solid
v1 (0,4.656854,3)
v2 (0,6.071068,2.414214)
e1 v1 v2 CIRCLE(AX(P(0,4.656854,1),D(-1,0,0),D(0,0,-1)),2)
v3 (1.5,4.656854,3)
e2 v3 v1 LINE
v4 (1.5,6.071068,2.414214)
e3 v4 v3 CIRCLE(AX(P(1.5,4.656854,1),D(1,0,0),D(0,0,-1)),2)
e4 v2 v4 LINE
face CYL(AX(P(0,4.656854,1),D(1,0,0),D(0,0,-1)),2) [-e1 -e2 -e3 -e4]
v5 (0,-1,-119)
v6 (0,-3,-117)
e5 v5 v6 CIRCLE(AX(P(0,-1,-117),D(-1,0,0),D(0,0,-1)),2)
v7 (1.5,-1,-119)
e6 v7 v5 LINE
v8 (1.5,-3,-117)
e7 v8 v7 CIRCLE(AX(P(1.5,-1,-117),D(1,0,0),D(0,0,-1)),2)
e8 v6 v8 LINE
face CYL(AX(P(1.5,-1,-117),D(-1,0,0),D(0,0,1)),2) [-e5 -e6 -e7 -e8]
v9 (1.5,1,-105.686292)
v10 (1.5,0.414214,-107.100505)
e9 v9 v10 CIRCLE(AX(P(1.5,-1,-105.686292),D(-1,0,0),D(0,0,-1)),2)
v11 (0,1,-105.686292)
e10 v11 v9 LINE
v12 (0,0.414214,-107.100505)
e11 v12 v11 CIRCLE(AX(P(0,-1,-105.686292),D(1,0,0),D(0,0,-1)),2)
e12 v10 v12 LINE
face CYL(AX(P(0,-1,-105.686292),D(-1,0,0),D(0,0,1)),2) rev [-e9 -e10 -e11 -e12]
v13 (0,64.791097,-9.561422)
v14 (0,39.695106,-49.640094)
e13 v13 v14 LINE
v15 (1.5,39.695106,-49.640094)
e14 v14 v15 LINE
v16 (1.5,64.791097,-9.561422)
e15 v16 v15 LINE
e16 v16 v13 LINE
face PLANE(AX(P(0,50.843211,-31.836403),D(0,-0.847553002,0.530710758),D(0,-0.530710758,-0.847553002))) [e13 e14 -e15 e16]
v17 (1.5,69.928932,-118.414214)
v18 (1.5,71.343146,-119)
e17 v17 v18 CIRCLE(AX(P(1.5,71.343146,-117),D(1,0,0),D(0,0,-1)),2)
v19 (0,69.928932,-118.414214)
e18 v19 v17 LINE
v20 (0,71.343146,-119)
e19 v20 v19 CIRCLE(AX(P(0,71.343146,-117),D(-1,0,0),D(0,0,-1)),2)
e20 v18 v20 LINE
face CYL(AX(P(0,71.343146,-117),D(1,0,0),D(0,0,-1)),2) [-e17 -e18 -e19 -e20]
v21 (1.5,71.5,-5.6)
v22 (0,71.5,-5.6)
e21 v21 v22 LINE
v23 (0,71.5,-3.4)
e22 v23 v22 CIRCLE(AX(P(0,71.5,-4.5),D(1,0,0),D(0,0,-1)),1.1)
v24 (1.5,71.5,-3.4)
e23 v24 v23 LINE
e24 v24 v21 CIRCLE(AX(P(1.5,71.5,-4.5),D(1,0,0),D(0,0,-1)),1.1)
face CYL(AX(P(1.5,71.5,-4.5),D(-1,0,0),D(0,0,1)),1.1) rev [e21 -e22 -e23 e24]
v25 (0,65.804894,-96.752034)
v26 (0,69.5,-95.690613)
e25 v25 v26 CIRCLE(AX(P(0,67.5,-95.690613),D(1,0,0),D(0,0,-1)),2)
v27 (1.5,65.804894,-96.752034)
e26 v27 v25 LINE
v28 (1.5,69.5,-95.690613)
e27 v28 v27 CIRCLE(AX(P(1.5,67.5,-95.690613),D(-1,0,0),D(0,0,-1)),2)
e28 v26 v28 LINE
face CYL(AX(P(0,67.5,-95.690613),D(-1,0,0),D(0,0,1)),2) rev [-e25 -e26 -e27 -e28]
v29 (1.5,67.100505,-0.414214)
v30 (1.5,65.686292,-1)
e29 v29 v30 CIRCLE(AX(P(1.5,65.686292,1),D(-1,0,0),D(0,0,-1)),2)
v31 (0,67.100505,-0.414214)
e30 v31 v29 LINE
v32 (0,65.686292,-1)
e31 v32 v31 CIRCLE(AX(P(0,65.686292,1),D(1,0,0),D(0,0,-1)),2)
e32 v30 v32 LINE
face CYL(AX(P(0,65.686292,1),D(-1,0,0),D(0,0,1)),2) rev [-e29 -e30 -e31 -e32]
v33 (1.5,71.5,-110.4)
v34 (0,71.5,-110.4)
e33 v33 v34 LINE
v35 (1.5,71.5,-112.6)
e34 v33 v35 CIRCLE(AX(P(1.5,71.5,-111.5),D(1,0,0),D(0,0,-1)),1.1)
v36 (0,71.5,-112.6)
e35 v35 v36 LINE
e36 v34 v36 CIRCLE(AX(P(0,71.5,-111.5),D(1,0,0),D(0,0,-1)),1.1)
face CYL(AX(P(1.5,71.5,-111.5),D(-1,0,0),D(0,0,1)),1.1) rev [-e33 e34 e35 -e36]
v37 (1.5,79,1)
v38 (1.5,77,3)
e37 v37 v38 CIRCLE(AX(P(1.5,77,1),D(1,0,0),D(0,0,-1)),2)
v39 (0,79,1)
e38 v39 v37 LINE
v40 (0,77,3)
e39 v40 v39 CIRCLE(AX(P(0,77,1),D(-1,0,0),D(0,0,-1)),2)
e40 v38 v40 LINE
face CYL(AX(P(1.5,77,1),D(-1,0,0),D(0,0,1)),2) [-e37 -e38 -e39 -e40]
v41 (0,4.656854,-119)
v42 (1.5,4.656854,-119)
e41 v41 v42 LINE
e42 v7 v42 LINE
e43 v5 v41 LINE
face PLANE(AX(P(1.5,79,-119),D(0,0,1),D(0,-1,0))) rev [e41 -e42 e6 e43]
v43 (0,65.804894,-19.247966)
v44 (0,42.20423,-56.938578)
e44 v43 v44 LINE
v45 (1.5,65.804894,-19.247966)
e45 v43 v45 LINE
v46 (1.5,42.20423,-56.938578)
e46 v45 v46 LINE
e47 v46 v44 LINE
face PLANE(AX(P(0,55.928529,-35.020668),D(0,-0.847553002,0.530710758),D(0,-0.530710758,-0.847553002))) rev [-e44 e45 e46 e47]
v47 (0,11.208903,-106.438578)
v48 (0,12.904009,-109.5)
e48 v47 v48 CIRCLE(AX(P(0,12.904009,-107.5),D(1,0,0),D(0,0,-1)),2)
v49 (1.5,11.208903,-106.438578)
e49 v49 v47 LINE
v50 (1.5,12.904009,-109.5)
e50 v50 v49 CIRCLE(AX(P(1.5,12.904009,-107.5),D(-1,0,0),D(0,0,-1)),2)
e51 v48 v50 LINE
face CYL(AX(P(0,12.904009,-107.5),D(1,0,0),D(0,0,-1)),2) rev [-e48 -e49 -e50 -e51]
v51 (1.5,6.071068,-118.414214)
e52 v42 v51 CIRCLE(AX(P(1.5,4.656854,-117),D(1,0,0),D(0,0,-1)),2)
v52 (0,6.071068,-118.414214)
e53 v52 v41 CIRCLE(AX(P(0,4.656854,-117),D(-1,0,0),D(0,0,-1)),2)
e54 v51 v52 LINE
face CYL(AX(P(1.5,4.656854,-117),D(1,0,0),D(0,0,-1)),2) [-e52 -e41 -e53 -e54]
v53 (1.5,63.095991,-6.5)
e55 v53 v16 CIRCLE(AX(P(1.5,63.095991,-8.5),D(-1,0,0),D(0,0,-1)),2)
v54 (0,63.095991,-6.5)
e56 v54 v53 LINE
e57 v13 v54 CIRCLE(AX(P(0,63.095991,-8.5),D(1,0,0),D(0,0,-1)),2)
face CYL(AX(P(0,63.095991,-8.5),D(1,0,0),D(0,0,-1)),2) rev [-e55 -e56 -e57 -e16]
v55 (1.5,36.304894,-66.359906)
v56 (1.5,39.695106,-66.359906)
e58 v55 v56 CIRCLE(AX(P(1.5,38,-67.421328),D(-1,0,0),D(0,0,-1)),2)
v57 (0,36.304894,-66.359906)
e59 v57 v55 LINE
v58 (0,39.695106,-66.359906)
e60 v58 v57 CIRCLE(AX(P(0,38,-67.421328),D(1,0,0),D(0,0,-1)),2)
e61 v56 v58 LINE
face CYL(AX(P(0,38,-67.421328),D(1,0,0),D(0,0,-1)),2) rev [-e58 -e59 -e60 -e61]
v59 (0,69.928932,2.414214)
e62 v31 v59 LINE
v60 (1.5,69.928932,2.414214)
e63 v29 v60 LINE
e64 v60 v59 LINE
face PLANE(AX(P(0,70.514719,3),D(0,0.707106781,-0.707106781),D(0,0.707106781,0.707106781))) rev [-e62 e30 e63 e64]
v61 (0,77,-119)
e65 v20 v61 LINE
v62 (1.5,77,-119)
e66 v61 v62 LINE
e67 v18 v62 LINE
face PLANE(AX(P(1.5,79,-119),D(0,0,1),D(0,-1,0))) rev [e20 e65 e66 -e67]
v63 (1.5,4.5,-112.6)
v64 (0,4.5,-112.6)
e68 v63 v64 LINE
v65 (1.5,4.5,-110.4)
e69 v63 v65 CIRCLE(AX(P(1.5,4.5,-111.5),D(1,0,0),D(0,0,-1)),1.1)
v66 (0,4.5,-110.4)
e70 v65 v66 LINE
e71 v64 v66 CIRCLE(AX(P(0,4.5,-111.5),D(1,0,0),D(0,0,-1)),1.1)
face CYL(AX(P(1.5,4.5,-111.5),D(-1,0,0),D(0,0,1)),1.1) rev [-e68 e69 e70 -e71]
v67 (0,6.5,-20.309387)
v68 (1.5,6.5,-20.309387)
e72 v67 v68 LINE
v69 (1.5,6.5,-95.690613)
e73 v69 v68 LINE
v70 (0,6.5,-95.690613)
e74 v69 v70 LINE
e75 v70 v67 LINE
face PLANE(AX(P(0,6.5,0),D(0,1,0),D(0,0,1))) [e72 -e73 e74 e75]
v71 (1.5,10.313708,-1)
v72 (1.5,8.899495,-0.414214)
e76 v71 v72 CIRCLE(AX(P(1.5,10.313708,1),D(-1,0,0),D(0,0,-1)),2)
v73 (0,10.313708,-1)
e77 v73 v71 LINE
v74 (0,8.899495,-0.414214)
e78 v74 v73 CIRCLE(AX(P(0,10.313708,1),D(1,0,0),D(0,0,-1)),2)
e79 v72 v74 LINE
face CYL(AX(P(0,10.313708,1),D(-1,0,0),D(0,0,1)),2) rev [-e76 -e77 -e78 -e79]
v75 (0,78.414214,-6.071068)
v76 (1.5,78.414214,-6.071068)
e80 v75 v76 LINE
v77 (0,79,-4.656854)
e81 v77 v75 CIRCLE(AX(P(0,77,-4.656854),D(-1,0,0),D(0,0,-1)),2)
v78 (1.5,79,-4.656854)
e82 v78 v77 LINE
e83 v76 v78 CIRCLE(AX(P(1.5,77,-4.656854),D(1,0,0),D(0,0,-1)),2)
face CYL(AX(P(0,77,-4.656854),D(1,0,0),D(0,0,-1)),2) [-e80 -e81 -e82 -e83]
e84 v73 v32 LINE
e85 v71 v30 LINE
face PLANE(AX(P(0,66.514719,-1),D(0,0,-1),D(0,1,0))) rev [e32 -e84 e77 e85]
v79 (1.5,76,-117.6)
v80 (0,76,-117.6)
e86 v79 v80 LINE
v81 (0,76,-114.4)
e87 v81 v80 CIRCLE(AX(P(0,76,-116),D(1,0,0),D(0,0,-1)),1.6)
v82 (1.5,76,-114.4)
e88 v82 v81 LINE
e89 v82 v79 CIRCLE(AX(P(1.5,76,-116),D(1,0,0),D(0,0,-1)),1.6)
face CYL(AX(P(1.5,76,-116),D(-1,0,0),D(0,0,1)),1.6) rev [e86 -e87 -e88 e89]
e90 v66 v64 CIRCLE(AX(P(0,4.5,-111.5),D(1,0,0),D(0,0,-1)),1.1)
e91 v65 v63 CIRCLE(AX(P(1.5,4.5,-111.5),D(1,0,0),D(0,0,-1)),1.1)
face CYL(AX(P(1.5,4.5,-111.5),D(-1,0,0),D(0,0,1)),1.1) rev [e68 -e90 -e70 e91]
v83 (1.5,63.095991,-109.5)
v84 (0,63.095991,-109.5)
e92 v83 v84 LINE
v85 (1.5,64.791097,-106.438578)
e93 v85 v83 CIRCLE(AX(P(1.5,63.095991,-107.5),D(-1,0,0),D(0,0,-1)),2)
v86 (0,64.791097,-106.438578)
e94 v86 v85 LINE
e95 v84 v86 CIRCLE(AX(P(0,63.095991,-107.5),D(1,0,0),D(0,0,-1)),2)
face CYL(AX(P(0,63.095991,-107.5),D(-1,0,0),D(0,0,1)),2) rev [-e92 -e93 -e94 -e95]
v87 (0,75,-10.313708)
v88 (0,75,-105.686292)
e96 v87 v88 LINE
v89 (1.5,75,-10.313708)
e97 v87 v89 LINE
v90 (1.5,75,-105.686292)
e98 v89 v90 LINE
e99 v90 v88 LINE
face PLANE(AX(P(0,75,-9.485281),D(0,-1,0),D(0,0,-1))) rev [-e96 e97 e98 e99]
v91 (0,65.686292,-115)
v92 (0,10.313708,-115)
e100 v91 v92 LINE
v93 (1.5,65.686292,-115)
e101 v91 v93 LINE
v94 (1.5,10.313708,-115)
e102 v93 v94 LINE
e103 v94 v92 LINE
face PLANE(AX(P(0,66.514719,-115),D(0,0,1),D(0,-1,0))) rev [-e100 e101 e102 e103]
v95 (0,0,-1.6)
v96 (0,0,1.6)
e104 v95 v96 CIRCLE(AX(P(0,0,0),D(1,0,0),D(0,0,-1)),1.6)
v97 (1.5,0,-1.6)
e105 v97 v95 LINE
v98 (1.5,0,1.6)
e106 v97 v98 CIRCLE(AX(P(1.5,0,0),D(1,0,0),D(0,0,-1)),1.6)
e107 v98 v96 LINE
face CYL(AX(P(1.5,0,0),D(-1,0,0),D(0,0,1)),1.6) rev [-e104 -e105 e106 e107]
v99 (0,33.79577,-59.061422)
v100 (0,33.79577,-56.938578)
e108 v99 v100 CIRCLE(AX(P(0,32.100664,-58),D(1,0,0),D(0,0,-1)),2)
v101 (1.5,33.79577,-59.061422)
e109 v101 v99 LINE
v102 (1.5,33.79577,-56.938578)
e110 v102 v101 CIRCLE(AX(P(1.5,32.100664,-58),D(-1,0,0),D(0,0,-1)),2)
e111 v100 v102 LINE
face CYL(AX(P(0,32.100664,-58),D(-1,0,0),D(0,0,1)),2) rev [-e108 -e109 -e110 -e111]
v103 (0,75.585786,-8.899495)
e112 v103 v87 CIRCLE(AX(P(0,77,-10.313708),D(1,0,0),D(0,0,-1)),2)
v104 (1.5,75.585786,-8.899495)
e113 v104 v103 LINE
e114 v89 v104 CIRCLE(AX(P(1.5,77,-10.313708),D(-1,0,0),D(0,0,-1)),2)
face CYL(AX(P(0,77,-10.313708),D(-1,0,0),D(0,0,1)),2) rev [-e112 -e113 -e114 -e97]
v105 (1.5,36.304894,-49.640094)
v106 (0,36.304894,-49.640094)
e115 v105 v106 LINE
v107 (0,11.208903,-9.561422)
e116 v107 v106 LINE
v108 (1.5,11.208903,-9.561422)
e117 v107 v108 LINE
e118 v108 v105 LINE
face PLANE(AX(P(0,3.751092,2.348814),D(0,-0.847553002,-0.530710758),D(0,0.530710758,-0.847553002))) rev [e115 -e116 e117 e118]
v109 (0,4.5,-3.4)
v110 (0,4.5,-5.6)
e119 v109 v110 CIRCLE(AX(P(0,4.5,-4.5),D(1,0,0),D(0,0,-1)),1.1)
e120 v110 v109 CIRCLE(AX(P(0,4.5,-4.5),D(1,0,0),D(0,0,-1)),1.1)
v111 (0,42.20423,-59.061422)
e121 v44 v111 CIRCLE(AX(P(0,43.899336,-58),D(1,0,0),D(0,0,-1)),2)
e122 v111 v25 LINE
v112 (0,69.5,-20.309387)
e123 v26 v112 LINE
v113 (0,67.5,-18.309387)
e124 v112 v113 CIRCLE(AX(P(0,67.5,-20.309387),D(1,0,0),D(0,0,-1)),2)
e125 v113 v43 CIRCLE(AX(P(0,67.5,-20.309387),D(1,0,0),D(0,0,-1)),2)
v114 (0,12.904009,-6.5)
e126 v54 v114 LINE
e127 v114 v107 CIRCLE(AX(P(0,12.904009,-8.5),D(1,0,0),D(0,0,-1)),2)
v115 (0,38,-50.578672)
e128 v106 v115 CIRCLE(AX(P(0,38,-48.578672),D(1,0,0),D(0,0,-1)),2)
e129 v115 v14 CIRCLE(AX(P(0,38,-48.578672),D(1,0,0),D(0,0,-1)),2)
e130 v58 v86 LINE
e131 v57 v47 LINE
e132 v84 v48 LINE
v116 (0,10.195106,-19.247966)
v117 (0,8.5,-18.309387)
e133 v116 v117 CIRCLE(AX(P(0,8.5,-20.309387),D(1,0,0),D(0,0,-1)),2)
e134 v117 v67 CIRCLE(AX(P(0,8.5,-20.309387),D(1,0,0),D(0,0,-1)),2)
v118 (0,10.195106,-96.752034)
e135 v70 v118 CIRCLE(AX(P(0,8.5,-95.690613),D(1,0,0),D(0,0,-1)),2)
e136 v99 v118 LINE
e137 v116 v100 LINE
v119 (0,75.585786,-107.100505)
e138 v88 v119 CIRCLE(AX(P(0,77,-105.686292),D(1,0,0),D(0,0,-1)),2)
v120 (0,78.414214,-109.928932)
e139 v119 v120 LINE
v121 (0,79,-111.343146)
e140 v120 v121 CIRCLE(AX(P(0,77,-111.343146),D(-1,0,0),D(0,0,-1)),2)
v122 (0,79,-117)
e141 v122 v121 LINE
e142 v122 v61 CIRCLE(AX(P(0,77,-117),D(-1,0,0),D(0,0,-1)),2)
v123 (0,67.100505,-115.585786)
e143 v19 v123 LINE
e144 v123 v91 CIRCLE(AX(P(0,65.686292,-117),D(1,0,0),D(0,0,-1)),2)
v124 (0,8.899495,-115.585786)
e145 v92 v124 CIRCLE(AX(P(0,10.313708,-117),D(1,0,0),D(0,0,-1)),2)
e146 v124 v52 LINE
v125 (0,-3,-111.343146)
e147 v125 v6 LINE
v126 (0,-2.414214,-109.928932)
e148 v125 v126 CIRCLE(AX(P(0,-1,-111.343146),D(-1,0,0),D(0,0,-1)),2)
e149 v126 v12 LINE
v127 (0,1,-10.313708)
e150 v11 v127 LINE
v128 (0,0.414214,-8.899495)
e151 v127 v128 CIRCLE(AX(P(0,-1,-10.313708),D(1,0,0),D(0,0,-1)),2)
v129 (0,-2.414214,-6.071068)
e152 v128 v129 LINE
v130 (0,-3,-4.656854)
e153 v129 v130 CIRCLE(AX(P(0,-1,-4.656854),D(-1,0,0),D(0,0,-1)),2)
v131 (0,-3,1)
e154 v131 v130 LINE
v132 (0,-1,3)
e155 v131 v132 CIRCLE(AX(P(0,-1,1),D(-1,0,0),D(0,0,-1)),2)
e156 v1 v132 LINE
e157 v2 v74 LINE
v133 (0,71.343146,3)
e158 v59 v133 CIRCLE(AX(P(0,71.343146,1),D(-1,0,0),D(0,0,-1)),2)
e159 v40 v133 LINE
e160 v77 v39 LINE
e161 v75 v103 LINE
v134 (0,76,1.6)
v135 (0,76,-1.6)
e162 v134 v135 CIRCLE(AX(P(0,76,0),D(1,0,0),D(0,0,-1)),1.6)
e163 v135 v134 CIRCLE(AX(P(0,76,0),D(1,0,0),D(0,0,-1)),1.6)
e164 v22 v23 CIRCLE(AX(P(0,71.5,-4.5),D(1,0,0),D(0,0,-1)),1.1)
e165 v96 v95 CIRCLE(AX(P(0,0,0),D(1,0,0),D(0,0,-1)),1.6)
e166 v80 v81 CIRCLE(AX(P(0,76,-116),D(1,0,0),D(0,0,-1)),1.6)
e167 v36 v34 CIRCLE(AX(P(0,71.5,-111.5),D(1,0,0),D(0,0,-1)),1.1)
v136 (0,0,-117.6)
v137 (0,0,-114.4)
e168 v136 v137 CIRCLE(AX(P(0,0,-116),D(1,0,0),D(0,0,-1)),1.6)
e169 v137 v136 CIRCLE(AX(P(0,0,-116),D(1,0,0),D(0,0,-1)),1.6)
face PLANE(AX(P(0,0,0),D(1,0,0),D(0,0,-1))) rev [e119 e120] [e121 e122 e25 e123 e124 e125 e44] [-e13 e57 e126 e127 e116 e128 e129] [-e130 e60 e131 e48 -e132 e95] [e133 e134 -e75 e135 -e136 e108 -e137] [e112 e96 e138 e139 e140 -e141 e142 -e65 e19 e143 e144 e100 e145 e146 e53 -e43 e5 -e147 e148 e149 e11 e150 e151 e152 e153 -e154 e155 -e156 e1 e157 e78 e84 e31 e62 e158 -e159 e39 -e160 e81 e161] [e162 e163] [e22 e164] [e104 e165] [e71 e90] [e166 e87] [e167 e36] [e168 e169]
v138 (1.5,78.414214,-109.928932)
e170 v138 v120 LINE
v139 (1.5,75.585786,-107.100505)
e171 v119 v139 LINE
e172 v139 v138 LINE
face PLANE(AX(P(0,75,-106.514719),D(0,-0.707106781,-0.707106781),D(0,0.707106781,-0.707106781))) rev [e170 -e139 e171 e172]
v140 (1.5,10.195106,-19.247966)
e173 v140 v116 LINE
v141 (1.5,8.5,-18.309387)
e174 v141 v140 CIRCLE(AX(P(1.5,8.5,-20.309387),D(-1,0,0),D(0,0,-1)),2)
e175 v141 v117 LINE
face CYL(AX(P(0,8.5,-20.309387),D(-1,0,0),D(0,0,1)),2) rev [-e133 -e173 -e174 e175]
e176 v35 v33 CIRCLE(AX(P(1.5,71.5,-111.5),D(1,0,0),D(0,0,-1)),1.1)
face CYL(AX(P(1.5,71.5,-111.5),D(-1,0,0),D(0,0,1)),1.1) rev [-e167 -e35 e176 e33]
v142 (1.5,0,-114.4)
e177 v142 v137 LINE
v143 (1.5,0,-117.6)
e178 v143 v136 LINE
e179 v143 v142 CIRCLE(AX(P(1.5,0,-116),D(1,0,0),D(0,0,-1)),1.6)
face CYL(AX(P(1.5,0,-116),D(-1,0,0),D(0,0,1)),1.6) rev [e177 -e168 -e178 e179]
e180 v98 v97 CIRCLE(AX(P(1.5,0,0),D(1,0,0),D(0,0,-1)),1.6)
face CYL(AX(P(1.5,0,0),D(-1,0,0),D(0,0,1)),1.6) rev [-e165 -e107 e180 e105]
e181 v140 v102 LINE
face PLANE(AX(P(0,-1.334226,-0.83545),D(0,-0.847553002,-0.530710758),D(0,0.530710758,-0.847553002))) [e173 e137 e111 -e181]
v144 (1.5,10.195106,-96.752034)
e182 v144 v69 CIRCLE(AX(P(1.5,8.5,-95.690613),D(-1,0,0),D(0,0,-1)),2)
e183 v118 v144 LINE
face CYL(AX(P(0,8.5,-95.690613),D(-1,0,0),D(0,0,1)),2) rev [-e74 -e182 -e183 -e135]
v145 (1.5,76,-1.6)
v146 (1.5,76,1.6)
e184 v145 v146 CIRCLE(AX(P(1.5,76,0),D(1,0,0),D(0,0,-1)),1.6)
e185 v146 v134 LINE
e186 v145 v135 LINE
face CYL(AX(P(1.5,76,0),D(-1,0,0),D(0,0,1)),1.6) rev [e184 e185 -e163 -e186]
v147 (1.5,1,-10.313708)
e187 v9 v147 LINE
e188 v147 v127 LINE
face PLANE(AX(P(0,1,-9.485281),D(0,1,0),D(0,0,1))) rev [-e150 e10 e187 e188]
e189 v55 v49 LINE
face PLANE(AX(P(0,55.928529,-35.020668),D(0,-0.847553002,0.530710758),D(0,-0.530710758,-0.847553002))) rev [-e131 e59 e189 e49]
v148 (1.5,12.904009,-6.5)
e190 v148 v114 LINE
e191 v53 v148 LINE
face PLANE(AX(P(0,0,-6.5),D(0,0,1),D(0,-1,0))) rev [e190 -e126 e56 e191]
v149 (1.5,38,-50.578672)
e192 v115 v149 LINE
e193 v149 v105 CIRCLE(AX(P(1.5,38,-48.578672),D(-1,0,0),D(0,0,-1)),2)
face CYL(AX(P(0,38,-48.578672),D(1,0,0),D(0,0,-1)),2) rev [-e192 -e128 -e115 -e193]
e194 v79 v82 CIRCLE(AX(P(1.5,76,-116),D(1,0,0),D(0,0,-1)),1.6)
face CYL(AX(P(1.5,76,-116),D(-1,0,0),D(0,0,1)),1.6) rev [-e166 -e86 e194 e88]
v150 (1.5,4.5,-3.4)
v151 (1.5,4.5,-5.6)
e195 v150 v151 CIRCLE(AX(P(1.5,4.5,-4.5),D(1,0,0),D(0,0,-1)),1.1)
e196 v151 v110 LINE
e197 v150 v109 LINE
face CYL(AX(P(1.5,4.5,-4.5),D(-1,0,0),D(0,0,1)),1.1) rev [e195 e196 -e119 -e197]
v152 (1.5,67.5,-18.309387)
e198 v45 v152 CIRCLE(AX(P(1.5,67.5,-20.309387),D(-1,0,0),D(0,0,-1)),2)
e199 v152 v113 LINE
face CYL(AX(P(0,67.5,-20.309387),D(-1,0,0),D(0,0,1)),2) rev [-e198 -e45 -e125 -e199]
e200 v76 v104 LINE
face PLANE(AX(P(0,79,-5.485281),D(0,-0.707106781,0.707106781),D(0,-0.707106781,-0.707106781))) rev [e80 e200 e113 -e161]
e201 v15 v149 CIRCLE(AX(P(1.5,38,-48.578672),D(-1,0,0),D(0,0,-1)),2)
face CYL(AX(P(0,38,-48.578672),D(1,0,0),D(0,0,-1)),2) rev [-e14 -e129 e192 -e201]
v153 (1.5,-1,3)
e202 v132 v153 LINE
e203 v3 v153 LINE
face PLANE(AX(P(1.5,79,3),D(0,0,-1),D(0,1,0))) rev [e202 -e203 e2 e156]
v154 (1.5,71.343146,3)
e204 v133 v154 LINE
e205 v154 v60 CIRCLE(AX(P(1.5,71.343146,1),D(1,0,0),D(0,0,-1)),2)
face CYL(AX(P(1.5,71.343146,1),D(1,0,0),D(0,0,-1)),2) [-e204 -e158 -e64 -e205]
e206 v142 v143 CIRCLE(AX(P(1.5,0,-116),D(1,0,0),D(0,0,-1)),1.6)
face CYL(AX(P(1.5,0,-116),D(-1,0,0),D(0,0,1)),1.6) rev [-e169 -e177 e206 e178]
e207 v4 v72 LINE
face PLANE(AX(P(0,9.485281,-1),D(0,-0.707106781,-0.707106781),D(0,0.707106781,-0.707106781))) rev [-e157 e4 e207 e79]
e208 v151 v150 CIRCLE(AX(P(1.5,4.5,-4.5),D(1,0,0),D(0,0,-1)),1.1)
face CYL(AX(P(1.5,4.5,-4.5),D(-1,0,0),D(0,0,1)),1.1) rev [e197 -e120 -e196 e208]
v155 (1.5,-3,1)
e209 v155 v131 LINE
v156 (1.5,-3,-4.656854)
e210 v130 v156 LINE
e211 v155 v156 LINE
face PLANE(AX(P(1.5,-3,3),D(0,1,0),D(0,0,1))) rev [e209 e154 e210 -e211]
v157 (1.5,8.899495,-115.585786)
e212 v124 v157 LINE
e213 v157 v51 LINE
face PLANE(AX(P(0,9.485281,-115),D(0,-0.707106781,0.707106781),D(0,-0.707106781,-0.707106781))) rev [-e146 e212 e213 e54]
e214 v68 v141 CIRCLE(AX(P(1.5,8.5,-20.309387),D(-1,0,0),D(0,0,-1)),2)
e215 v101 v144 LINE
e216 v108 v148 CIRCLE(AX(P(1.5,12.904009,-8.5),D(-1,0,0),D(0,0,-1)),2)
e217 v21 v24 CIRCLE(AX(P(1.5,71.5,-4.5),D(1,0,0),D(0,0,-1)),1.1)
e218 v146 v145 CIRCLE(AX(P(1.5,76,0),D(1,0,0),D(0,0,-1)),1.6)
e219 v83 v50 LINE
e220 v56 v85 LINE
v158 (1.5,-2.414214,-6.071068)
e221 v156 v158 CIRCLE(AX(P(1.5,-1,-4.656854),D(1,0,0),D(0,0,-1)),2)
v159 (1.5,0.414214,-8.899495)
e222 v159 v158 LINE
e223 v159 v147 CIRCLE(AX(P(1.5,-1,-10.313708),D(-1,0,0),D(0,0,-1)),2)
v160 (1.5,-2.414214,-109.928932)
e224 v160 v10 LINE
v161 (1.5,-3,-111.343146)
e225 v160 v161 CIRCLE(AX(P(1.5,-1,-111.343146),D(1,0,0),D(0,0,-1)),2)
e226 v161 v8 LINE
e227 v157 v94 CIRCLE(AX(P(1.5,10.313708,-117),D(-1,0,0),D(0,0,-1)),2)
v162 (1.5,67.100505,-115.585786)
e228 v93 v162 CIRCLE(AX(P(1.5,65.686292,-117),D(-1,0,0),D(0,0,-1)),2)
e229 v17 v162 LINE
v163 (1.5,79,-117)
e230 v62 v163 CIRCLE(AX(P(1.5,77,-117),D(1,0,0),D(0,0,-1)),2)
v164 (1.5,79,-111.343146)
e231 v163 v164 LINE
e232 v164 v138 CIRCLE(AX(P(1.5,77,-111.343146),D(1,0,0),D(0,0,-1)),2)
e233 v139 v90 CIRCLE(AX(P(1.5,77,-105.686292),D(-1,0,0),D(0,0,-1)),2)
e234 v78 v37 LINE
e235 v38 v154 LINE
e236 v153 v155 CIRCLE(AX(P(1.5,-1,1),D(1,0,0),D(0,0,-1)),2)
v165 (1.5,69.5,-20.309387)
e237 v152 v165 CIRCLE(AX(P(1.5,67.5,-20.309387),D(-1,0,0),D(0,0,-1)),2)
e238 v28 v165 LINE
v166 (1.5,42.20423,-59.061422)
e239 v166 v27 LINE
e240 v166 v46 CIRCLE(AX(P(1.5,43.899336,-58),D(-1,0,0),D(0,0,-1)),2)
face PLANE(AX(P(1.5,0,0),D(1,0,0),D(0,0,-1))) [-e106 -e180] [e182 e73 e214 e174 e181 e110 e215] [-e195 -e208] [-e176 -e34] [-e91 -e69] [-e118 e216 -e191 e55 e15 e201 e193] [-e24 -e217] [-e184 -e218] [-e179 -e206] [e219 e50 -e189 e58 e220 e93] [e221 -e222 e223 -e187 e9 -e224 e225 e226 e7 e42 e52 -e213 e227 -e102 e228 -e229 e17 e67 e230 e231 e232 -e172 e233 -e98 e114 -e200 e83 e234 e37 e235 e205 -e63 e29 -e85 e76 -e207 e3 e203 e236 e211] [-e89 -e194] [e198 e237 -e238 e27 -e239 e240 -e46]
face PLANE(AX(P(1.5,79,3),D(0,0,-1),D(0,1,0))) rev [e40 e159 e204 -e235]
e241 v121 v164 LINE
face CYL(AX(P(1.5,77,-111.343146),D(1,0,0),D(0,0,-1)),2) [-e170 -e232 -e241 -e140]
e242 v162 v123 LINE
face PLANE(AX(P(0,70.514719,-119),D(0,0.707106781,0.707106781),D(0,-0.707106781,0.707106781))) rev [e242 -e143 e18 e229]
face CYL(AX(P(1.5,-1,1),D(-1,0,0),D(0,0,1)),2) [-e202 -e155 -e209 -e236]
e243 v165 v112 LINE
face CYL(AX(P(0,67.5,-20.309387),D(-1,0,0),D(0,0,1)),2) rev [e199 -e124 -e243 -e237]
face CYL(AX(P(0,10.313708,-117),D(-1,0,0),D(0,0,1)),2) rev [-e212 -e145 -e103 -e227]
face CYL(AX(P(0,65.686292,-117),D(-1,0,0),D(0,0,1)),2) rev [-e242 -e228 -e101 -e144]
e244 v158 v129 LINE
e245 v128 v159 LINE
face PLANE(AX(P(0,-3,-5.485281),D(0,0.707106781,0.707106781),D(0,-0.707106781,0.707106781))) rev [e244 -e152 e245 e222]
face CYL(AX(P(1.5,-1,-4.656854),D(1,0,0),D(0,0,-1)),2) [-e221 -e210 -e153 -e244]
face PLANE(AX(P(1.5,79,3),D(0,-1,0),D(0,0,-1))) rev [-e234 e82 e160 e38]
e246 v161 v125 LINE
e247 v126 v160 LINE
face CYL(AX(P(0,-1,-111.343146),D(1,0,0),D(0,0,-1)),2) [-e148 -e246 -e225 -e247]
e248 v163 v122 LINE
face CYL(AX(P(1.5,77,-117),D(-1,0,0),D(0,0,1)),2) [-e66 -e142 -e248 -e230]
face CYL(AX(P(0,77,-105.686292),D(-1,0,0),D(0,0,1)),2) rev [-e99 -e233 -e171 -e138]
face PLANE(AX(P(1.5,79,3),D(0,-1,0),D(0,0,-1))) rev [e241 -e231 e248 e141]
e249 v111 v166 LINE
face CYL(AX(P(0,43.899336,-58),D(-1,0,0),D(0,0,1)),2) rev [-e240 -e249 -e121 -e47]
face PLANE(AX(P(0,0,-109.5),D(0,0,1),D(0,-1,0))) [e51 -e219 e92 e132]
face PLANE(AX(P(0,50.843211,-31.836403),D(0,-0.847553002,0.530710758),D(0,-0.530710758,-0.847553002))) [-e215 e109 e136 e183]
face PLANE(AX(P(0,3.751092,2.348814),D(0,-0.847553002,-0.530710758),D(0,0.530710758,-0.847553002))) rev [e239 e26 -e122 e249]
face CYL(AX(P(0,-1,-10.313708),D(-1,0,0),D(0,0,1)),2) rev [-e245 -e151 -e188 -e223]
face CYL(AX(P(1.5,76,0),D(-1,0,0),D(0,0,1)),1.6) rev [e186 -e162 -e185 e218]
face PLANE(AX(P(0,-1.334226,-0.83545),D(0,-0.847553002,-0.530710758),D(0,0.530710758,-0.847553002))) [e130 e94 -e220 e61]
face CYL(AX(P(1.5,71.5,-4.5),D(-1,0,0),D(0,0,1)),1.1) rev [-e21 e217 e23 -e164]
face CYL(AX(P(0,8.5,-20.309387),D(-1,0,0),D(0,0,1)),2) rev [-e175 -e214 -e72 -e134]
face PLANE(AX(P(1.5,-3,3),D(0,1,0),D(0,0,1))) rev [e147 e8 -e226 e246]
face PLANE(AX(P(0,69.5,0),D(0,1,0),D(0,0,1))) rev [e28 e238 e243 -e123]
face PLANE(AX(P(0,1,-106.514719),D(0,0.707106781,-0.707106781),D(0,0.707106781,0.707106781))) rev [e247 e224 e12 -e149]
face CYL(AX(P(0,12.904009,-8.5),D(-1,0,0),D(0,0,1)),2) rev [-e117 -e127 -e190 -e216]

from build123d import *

# Parameters (mm, degrees)
SKETCH_1_W          = 122
SKETCH_1_H          = 82
SKETCH_1_R          = 1.6
SKETCH_1_R_2        = 1.1
EXTRUDE_1_DEPTH     = 1.5
CUT_EXTRUDE_1_DEPTH = 143.843445772
CUT_EXTRUDE_2_DEPTH = 143.843445772
FILLET_1_R          = 2


with BuildPart() as part:
    # 草图1 → 凸台-拉伸1 (new body)
    with BuildSketch(Plane(origin=(0, 0, 0), x_dir=(0, 0, -1), z_dir=(1, 0, 0))):
        with Locations((58, 38)):
            Rectangle(SKETCH_1_W, SKETCH_1_H)
        with Locations((0, 76)):
            Circle(SKETCH_1_R, mode=Mode.SUBTRACT)
        Circle(SKETCH_1_R, mode=Mode.SUBTRACT)
        with Locations((116, 76)):
            Circle(SKETCH_1_R, mode=Mode.SUBTRACT)
        with Locations((116, 0)):
            Circle(SKETCH_1_R, mode=Mode.SUBTRACT)
        with Locations((4.5, 71.5)):
            Circle(SKETCH_1_R_2, mode=Mode.SUBTRACT)
        with Locations((4.5, 4.5)):
            Circle(SKETCH_1_R_2, mode=Mode.SUBTRACT)
        with Locations((111.5, 71.5)):
            Circle(SKETCH_1_R_2, mode=Mode.SUBTRACT)
        with Locations((111.5, 4.5)):
            Circle(SKETCH_1_R_2, mode=Mode.SUBTRACT)
    extrude(amount=EXTRUDE_1_DEPTH)

    # 草图2 → 切除-拉伸1 (cut, through all)
    with BuildSketch(Plane(origin=(1.5, 0, 0), x_dir=(0, 0, -1), z_dir=(1, 0, 0))):
        Polygon((102.653173492, 69.5), (13.346826508, 69.5), (58, 41.539601645), align=None)
        Polygon((52.347203343, 38), (6.5, 66.708061906), (6.5, 9.291938094), align=None)
        Polygon((102.653173492, 6.5), (58, 34.460398355), (13.346826508, 6.5), align=None)
        Polygon((109.5, 66.708061906), (63.652796657, 38), (109.5, 9.291938094), align=None)
    extrude(amount=-CUT_EXTRUDE_1_DEPTH, mode=Mode.SUBTRACT)

    # 草图3 → 切除-拉伸2 (cut, through all)
    with BuildSketch(Plane(origin=(1.5, 0, 0), x_dir=(0, 0, -1), z_dir=(1, 0, 0))):
        Polygon((5.485281374, 79), (9.485281374, 75), (106.514718626, 75), (110.514718626, 79), align=None)
        Polygon((106.514718626, 1), (110.514718626, -3), (5.485281374, -3), (9.485281374, 1), align=None)
        Polygon((-3, 70.514718626), (1, 66.514718626), (1, 9.485281374), (-3, 5.485281374), align=None)
        Polygon((115, 9.485281374), (119, 5.485281374), (119, 70.514718626), (115, 66.514718626), align=None)
    extrude(amount=-CUT_EXTRUDE_2_DEPTH, mode=Mode.SUBTRACT)

    # 圆角1
    fillet_1_edges = [part.edges().sort_by_distance(p)[0] for p in [
        (0.75, 79, -5.485281374),
        (0.75, 79, -110.514718626),
        (0.75, 75, -106.514718626),
        (0.75, 75, -9.485281374),
        (0.75, 1, -9.485281374),
        (0.75, 1, -106.514718626),
        (0.75, -3, -110.514718626),
        (0.75, -3, -5.485281374),
        (0.75, 5.485281374, 3),
        (0.75, 70.514718626, 3),
        (0.75, 66.514718626, -1),
        (0.75, 9.485281374, -1),
        (0.75, 9.485281374, -115),
        (0.75, 66.514718626, -115),
        (0.75, 70.514718626, -119),
        (0.75, 5.485281374, -119),
        (0.75, 6.5, -102.653173492),
        (0.75, 6.5, -13.346826508),
        (0.75, 34.460398355, -58),
        (0.75, 9.291938094, -6.5),
        (0.75, 66.708061906, -6.5),
        (0.75, 38, -52.347203343),
        (0.75, 66.708061906, -109.5),
        (0.75, 9.291938094, -109.5),
        (0.75, 38, -63.652796657),
        (0.75, 69.5, -102.653173492),
        (0.75, 41.539601645, -58),
        (0.75, 69.5, -13.346826508),
        (0.75, 79, 3),
        (0.75, 79, -119),
        (0.75, -3, -119),
        (0.75, -3, 3),
    ]]
    fillet(fillet_1_edges, radius=FILLET_1_R)


solid = part.part
